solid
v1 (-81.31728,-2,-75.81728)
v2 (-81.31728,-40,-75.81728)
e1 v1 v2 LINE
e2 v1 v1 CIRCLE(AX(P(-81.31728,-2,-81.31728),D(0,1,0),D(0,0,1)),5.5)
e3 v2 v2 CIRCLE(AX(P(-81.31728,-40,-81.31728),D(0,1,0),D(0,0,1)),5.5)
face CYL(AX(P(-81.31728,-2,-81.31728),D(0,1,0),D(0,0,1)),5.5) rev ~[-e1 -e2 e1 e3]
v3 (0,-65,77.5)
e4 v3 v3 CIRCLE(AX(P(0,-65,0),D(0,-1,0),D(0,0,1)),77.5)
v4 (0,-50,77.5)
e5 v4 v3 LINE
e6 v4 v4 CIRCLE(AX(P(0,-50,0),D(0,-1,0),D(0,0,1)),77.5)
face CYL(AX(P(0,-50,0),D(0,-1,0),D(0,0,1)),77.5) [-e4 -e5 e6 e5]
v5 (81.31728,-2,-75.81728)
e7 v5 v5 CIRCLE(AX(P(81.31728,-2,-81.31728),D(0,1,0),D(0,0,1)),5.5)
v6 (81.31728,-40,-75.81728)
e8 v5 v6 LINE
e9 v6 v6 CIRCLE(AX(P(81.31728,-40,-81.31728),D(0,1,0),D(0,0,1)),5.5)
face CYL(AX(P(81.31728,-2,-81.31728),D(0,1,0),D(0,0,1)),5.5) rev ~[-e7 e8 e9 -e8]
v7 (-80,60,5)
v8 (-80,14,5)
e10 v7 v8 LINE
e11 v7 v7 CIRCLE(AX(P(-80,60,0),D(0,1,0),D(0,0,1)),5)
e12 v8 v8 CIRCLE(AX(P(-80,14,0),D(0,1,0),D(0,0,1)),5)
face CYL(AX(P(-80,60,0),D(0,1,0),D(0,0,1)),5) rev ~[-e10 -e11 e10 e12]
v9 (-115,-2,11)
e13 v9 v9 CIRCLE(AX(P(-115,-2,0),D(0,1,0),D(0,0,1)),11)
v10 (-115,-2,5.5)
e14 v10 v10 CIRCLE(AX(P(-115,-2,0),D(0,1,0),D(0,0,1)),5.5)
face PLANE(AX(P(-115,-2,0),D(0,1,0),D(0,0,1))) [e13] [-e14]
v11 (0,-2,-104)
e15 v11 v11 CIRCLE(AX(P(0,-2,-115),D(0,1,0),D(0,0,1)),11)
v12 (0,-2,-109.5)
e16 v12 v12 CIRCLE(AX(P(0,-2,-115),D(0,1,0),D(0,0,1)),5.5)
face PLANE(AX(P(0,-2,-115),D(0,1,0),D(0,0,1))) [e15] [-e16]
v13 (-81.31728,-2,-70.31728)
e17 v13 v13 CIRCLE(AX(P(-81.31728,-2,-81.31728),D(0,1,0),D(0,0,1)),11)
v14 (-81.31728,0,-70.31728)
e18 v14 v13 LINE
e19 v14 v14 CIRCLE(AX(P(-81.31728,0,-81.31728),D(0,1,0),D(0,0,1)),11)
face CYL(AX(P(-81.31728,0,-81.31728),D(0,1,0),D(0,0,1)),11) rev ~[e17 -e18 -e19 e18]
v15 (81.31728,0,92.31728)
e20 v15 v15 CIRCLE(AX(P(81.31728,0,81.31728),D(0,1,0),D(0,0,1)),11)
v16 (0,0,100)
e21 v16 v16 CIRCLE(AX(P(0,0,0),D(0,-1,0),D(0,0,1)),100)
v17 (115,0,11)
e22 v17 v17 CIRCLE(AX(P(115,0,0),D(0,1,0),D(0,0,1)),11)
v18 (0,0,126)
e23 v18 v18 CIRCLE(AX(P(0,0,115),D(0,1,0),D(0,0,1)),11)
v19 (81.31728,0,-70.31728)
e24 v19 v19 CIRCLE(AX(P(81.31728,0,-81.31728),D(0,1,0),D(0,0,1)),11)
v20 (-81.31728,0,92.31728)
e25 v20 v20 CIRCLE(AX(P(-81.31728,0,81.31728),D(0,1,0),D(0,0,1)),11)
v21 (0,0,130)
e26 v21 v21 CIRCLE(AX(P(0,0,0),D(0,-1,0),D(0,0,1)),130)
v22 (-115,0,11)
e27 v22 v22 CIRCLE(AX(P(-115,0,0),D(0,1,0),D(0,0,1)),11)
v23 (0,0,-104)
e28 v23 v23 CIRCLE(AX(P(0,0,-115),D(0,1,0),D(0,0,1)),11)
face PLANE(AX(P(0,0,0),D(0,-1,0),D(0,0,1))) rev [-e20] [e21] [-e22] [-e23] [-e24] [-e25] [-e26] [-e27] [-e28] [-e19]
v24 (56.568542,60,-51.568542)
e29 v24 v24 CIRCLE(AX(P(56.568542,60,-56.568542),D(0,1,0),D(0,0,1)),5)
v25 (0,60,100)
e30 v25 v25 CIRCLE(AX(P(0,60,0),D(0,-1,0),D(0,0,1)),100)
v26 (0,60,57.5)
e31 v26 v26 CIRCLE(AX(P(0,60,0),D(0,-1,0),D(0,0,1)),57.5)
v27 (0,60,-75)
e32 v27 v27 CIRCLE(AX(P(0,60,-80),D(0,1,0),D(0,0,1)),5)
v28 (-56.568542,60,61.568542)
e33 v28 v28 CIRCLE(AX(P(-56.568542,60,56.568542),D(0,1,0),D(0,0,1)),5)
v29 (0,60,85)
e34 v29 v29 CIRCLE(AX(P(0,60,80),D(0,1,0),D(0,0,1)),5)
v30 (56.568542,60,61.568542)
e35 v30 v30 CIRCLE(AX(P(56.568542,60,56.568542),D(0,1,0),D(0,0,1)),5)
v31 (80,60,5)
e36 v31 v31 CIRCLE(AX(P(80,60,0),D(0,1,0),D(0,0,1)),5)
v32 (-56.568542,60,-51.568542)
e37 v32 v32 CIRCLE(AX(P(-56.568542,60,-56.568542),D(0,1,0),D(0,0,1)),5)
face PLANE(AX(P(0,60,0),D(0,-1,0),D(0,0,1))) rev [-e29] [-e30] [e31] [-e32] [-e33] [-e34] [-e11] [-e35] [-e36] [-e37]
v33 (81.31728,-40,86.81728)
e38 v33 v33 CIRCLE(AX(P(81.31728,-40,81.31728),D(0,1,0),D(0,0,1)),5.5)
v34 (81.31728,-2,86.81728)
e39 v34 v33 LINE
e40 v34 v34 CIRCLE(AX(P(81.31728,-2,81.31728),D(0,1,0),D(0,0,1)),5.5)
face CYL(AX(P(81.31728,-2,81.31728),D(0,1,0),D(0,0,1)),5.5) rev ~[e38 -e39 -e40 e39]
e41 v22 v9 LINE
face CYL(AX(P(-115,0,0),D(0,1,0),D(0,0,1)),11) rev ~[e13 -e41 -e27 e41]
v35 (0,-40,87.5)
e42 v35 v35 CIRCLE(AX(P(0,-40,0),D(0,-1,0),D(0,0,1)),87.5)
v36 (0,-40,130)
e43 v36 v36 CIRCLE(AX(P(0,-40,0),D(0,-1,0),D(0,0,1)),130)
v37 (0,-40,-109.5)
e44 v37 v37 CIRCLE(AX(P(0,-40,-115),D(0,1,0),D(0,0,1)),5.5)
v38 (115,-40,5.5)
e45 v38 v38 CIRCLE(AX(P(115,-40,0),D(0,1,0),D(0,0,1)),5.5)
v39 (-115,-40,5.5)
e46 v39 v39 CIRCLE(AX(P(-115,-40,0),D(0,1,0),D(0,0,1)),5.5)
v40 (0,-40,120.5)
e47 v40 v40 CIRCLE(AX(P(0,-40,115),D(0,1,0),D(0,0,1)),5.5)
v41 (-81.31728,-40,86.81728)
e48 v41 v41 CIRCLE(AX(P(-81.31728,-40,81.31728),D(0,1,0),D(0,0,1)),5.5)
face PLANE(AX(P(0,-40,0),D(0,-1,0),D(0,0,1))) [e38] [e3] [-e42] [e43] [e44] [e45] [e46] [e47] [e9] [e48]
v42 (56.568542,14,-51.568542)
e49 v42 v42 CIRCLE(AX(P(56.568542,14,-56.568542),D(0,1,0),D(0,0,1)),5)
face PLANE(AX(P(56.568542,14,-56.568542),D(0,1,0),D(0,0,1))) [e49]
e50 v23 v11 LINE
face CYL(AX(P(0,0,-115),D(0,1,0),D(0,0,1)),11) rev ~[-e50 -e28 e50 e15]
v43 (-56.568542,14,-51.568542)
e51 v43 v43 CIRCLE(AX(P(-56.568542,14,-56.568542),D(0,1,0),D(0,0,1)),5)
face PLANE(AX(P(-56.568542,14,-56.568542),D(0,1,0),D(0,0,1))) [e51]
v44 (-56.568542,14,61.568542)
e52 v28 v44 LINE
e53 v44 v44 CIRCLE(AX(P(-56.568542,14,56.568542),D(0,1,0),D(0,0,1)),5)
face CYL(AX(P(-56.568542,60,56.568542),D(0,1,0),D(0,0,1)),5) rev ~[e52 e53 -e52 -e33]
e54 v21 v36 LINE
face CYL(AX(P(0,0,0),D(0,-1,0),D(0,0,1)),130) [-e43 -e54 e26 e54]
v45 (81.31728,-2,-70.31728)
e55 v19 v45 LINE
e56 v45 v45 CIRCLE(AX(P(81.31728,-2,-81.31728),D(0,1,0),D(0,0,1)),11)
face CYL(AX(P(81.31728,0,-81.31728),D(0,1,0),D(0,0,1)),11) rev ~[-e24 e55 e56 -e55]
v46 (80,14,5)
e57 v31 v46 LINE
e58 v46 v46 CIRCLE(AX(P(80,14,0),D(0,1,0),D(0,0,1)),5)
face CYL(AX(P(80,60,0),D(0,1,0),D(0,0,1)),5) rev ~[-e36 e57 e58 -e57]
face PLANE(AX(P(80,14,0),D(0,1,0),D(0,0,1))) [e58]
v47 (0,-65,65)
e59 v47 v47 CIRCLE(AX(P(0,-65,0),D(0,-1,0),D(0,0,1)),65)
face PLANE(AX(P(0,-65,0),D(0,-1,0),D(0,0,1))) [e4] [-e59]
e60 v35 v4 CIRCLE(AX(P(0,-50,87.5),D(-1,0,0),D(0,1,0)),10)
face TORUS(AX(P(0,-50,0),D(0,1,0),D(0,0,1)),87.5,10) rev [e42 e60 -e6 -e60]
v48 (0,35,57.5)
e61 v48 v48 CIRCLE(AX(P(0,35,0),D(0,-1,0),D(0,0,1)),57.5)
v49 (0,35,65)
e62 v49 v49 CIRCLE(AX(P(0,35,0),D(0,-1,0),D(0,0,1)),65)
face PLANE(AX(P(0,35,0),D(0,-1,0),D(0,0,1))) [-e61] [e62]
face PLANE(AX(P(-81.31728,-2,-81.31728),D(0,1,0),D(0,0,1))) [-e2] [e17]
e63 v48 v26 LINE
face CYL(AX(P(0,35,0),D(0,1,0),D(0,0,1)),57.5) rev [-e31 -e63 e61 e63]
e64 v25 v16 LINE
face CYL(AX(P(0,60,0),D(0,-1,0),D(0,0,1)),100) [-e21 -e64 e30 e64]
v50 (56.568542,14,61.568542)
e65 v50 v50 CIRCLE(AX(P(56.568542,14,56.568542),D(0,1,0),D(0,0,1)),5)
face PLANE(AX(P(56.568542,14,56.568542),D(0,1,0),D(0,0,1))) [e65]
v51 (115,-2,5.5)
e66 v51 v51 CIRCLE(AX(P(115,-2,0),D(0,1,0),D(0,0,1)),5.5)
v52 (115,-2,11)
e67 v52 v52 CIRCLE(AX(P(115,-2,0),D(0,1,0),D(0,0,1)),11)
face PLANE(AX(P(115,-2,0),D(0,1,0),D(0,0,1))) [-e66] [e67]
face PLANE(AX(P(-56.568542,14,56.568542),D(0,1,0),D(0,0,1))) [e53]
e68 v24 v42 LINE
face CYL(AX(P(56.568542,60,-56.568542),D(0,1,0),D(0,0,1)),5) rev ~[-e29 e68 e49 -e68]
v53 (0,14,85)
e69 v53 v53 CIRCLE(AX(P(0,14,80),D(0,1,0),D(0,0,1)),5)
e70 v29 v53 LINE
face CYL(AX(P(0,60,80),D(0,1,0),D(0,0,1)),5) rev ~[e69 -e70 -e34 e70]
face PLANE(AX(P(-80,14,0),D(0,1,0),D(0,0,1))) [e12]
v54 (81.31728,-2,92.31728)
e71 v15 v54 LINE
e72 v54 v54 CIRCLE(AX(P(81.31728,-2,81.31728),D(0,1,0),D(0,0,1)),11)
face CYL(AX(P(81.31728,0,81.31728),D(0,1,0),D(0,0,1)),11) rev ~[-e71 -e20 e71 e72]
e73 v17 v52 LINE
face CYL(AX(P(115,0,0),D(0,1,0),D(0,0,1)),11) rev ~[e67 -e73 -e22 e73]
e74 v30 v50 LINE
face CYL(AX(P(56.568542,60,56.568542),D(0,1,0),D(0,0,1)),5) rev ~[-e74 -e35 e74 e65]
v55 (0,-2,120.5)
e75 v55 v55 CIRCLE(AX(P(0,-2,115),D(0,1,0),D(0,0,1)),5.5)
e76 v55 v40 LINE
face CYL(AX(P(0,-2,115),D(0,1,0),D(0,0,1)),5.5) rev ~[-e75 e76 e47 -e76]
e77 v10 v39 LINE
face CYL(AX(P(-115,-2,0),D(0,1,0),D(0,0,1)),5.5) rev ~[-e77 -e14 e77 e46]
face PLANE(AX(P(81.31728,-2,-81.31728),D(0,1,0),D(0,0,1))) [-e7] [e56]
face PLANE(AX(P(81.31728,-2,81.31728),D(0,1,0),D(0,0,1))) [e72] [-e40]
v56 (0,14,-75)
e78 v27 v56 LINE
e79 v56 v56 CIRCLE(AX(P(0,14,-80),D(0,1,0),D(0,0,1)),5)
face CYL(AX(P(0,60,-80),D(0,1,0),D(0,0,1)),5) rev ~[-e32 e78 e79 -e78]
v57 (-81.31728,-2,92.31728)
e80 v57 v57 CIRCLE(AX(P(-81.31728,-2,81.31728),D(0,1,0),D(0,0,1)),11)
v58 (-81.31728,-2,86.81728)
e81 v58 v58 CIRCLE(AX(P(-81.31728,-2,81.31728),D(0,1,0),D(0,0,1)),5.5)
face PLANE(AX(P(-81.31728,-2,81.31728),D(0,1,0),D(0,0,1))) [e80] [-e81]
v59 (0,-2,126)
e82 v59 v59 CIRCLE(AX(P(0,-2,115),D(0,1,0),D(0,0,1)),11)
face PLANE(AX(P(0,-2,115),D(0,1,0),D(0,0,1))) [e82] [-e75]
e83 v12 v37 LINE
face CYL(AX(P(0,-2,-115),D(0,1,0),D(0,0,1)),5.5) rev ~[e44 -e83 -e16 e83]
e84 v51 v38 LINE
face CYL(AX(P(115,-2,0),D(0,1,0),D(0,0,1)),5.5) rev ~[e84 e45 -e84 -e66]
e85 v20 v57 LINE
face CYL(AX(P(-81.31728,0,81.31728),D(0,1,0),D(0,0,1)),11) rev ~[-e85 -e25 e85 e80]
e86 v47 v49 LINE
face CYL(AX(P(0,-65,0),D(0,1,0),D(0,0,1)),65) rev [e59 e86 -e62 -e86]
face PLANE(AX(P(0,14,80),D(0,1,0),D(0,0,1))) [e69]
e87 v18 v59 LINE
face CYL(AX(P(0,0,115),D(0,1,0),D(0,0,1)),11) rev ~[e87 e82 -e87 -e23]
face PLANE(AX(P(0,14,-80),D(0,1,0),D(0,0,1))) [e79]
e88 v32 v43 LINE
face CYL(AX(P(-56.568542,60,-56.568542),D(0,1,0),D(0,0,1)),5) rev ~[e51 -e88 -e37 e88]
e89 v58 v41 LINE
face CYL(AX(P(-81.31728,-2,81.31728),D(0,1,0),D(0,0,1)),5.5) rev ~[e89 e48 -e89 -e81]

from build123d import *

# Parameters (mm, degrees)
SKETCH_2_R          = 11
CUT_EXTRUDE_1_DEPTH = 2
CUT_EXTRUDE_2_REACH = 196.342
SKETCH_3_R          = 5.5
SKETCH_4_R          = 5
CUT_EXTRUDE_3_DEPTH = 46


with BuildPart() as part:
    # 草图1 → 旋转1 (revolve)
    with BuildSketch(Plane.XY, mode=Mode.PRIVATE) as revolve_1_sk:
        with BuildLine():
            Line((65, 35), (57.5, 35))
            Line((57.5, 35), (57.5, 60))
            Line((57.5, 60), (100, 60))
            Line((100, 60), (100, 0))
            Line((100, 0), (130, 0))
            Line((130, 0), (130, -40))
            Line((130, -40), (87.5, -40))
            ThreePointArc((87.5, -40), (80.428932188, -42.928932188), (77.5, -50))
            Line((77.5, -50), (77.5, -65))
            Line((77.5, -65), (65, -65))
            Line((65, -65), (65, 35))
        make_face()
    revolve(revolve_1_sk.sketch.rotate(Axis((0, 133.6875, 0), (0, -1, 0)), 90), axis=Axis((0, 133.6875, 0), (0, -1, 0)))

    # 草图2 → 切除-拉伸1 (cut)
    with BuildSketch(Plane(origin=(0, 0, 0), x_dir=(1, 0, 0), z_dir=(0, 1, 0))):
        with Locations(Location((115, 0, 0), (0, 0, 270))):
            Circle(SKETCH_2_R)
        with Locations(Location((81.317279836, -81.317279836, 0), (0, 0, 270))):
            Circle(SKETCH_2_R)
        with Locations(Location((0, -115, 0), (0, 0, 270))):
            Circle(SKETCH_2_R)
        with Locations(Location((-81.317279836, -81.317279836, 0), (0, 0, 270))):
            Circle(SKETCH_2_R)
        with Locations(Location((-115, 0, 0), (0, 0, 270))):
            Circle(SKETCH_2_R)
        with Locations(Location((-81.317279836, 81.317279836, 0), (0, 0, 270))):
            Circle(SKETCH_2_R)
        with Locations(Location((0, 115, 0), (0, 0, 270))):
            Circle(SKETCH_2_R)
        with Locations(Location((81.317279836, 81.317279836, 0), (0, 0, 270))):
            Circle(SKETCH_2_R)
    extrude(amount=-CUT_EXTRUDE_1_DEPTH, mode=Mode.SUBTRACT)

    # 草图3 → 切除-拉伸2 (cut, up to next)
    with BuildSketch(Plane(origin=(0, -2, 0), x_dir=(1, 0, 0), z_dir=(0, 1, 0)), mode=Mode.PRIVATE) as cut_extrude_2_sk1:
        with Locations(Location((81.317279836, 81.317279836, 0), (0, 0, 270))):
            Circle(SKETCH_3_R)
    cut_extrude_2_tool1 = extrude(cut_extrude_2_sk1.sketch, amount=-CUT_EXTRUDE_2_REACH, mode=Mode.PRIVATE) & part.part
    # 草图3 → 切除-拉伸2 (cut, up to next)
    with BuildSketch(Plane(origin=(0, -2, 0), x_dir=(1, 0, 0), z_dir=(0, 1, 0)), mode=Mode.PRIVATE) as cut_extrude_2_sk2:
        with Locations(Location((115, 0, 0), (0, 0, 270))):
            Circle(SKETCH_3_R)
    cut_extrude_2_tool2 = extrude(cut_extrude_2_sk2.sketch, amount=-CUT_EXTRUDE_2_REACH, mode=Mode.PRIVATE) & part.part
    # 草图3 → 切除-拉伸2 (cut, up to next)
    with BuildSketch(Plane(origin=(0, -2, 0), x_dir=(1, 0, 0), z_dir=(0, 1, 0)), mode=Mode.PRIVATE) as cut_extrude_2_sk3:
        with Locations(Location((81.317279836, -81.317279836, 0), (0, 0, 270))):
            Circle(SKETCH_3_R)
    cut_extrude_2_tool3 = extrude(cut_extrude_2_sk3.sketch, amount=-CUT_EXTRUDE_2_REACH, mode=Mode.PRIVATE) & part.part
    # 草图3 → 切除-拉伸2 (cut, up to next)
    with BuildSketch(Plane(origin=(0, -2, 0), x_dir=(1, 0, 0), z_dir=(0, 1, 0)), mode=Mode.PRIVATE) as cut_extrude_2_sk4:
        with Locations(Location((0, -115, 0), (0, 0, 270))):
            Circle(SKETCH_3_R)
    cut_extrude_2_tool4 = extrude(cut_extrude_2_sk4.sketch, amount=-CUT_EXTRUDE_2_REACH, mode=Mode.PRIVATE) & part.part
    # 草图3 → 切除-拉伸2 (cut, up to next)
    with BuildSketch(Plane(origin=(0, -2, 0), x_dir=(1, 0, 0), z_dir=(0, 1, 0)), mode=Mode.PRIVATE) as cut_extrude_2_sk5:
        with Locations(Location((-81.317279836, -81.317279836, 0), (0, 0, 270))):
            Circle(SKETCH_3_R)
    cut_extrude_2_tool5 = extrude(cut_extrude_2_sk5.sketch, amount=-CUT_EXTRUDE_2_REACH, mode=Mode.PRIVATE) & part.part
    # 草图3 → 切除-拉伸2 (cut, up to next)
    with BuildSketch(Plane(origin=(0, -2, 0), x_dir=(1, 0, 0), z_dir=(0, 1, 0)), mode=Mode.PRIVATE) as cut_extrude_2_sk6:
        with Locations(Location((-115, 0, 0), (0, 0, 270))):
            Circle(SKETCH_3_R)
    cut_extrude_2_tool6 = extrude(cut_extrude_2_sk6.sketch, amount=-CUT_EXTRUDE_2_REACH, mode=Mode.PRIVATE) & part.part
    # 草图3 → 切除-拉伸2 (cut, up to next)
    with BuildSketch(Plane(origin=(0, -2, 0), x_dir=(1, 0, 0), z_dir=(0, 1, 0)), mode=Mode.PRIVATE) as cut_extrude_2_sk7:
        with Locations(Location((-81.317279836, 81.317279836, 0), (0, 0, 270))):
            Circle(SKETCH_3_R)
    cut_extrude_2_tool7 = extrude(cut_extrude_2_sk7.sketch, amount=-CUT_EXTRUDE_2_REACH, mode=Mode.PRIVATE) & part.part
    # 草图3 → 切除-拉伸2 (cut, up to next)
    with BuildSketch(Plane(origin=(0, -2, 0), x_dir=(1, 0, 0), z_dir=(0, 1, 0)), mode=Mode.PRIVATE) as cut_extrude_2_sk8:
        with Locations(Location((0, 115, 0), (0, 0, 270))):
            Circle(SKETCH_3_R)
    cut_extrude_2_tool8 = extrude(cut_extrude_2_sk8.sketch, amount=-CUT_EXTRUDE_2_REACH, mode=Mode.PRIVATE) & part.part
    add(cut_extrude_2_tool1.solids().sort_by_distance((81.31728, -2, -81.31728))[0], mode=Mode.SUBTRACT)
    add(cut_extrude_2_tool2.solids().sort_by_distance((115, -2, 0))[0], mode=Mode.SUBTRACT)
    add(cut_extrude_2_tool3.solids().sort_by_distance((81.31728, -2, 81.31728))[0], mode=Mode.SUBTRACT)
    add(cut_extrude_2_tool4.solids().sort_by_distance((0, -2, 115))[0], mode=Mode.SUBTRACT)
    add(cut_extrude_2_tool5.solids().sort_by_distance((-81.31728, -2, 81.31728))[0], mode=Mode.SUBTRACT)
    add(cut_extrude_2_tool6.solids().sort_by_distance((-115, -2, 0))[0], mode=Mode.SUBTRACT)
    add(cut_extrude_2_tool7.solids().sort_by_distance((-81.31728, -2, -81.31728))[0], mode=Mode.SUBTRACT)
    add(cut_extrude_2_tool8.solids().sort_by_distance((0, -2, -115))[0], mode=Mode.SUBTRACT)

    # 草图4 → 切除-拉伸3 (cut)
    with BuildSketch(Plane(origin=(0, 60, 0), x_dir=(1, 0, 0), z_dir=(0, 1, 0))):
        with Locations(Location((80, 0, 0), (0, 0, 270))):
            Circle(SKETCH_4_R)
        with Locations(Location((56.568542495, -56.568542495, 0), (0, 0, 270))):
            Circle(SKETCH_4_R)
        with Locations(Location((0, -80, 0), (0, 0, 270))):
            Circle(SKETCH_4_R)
        with Locations(Location((-56.568542495, -56.568542495, 0), (0, 0, 270))):
            Circle(SKETCH_4_R)
        with Locations(Location((-80, 0, 0), (0, 0, 270))):
            Circle(SKETCH_4_R)
        with Locations(Location((-56.568542495, 56.568542495, 0), (0, 0, 270))):
            Circle(SKETCH_4_R)
        with Locations(Location((0, 80, 0), (0, 0, 270))):
            Circle(SKETCH_4_R)
        with Locations(Location((56.568542495, 56.568542495, 0), (0, 0, 270))):
            Circle(SKETCH_4_R)
    extrude(amount=-CUT_EXTRUDE_3_DEPTH, mode=Mode.SUBTRACT)


solid = part.part
